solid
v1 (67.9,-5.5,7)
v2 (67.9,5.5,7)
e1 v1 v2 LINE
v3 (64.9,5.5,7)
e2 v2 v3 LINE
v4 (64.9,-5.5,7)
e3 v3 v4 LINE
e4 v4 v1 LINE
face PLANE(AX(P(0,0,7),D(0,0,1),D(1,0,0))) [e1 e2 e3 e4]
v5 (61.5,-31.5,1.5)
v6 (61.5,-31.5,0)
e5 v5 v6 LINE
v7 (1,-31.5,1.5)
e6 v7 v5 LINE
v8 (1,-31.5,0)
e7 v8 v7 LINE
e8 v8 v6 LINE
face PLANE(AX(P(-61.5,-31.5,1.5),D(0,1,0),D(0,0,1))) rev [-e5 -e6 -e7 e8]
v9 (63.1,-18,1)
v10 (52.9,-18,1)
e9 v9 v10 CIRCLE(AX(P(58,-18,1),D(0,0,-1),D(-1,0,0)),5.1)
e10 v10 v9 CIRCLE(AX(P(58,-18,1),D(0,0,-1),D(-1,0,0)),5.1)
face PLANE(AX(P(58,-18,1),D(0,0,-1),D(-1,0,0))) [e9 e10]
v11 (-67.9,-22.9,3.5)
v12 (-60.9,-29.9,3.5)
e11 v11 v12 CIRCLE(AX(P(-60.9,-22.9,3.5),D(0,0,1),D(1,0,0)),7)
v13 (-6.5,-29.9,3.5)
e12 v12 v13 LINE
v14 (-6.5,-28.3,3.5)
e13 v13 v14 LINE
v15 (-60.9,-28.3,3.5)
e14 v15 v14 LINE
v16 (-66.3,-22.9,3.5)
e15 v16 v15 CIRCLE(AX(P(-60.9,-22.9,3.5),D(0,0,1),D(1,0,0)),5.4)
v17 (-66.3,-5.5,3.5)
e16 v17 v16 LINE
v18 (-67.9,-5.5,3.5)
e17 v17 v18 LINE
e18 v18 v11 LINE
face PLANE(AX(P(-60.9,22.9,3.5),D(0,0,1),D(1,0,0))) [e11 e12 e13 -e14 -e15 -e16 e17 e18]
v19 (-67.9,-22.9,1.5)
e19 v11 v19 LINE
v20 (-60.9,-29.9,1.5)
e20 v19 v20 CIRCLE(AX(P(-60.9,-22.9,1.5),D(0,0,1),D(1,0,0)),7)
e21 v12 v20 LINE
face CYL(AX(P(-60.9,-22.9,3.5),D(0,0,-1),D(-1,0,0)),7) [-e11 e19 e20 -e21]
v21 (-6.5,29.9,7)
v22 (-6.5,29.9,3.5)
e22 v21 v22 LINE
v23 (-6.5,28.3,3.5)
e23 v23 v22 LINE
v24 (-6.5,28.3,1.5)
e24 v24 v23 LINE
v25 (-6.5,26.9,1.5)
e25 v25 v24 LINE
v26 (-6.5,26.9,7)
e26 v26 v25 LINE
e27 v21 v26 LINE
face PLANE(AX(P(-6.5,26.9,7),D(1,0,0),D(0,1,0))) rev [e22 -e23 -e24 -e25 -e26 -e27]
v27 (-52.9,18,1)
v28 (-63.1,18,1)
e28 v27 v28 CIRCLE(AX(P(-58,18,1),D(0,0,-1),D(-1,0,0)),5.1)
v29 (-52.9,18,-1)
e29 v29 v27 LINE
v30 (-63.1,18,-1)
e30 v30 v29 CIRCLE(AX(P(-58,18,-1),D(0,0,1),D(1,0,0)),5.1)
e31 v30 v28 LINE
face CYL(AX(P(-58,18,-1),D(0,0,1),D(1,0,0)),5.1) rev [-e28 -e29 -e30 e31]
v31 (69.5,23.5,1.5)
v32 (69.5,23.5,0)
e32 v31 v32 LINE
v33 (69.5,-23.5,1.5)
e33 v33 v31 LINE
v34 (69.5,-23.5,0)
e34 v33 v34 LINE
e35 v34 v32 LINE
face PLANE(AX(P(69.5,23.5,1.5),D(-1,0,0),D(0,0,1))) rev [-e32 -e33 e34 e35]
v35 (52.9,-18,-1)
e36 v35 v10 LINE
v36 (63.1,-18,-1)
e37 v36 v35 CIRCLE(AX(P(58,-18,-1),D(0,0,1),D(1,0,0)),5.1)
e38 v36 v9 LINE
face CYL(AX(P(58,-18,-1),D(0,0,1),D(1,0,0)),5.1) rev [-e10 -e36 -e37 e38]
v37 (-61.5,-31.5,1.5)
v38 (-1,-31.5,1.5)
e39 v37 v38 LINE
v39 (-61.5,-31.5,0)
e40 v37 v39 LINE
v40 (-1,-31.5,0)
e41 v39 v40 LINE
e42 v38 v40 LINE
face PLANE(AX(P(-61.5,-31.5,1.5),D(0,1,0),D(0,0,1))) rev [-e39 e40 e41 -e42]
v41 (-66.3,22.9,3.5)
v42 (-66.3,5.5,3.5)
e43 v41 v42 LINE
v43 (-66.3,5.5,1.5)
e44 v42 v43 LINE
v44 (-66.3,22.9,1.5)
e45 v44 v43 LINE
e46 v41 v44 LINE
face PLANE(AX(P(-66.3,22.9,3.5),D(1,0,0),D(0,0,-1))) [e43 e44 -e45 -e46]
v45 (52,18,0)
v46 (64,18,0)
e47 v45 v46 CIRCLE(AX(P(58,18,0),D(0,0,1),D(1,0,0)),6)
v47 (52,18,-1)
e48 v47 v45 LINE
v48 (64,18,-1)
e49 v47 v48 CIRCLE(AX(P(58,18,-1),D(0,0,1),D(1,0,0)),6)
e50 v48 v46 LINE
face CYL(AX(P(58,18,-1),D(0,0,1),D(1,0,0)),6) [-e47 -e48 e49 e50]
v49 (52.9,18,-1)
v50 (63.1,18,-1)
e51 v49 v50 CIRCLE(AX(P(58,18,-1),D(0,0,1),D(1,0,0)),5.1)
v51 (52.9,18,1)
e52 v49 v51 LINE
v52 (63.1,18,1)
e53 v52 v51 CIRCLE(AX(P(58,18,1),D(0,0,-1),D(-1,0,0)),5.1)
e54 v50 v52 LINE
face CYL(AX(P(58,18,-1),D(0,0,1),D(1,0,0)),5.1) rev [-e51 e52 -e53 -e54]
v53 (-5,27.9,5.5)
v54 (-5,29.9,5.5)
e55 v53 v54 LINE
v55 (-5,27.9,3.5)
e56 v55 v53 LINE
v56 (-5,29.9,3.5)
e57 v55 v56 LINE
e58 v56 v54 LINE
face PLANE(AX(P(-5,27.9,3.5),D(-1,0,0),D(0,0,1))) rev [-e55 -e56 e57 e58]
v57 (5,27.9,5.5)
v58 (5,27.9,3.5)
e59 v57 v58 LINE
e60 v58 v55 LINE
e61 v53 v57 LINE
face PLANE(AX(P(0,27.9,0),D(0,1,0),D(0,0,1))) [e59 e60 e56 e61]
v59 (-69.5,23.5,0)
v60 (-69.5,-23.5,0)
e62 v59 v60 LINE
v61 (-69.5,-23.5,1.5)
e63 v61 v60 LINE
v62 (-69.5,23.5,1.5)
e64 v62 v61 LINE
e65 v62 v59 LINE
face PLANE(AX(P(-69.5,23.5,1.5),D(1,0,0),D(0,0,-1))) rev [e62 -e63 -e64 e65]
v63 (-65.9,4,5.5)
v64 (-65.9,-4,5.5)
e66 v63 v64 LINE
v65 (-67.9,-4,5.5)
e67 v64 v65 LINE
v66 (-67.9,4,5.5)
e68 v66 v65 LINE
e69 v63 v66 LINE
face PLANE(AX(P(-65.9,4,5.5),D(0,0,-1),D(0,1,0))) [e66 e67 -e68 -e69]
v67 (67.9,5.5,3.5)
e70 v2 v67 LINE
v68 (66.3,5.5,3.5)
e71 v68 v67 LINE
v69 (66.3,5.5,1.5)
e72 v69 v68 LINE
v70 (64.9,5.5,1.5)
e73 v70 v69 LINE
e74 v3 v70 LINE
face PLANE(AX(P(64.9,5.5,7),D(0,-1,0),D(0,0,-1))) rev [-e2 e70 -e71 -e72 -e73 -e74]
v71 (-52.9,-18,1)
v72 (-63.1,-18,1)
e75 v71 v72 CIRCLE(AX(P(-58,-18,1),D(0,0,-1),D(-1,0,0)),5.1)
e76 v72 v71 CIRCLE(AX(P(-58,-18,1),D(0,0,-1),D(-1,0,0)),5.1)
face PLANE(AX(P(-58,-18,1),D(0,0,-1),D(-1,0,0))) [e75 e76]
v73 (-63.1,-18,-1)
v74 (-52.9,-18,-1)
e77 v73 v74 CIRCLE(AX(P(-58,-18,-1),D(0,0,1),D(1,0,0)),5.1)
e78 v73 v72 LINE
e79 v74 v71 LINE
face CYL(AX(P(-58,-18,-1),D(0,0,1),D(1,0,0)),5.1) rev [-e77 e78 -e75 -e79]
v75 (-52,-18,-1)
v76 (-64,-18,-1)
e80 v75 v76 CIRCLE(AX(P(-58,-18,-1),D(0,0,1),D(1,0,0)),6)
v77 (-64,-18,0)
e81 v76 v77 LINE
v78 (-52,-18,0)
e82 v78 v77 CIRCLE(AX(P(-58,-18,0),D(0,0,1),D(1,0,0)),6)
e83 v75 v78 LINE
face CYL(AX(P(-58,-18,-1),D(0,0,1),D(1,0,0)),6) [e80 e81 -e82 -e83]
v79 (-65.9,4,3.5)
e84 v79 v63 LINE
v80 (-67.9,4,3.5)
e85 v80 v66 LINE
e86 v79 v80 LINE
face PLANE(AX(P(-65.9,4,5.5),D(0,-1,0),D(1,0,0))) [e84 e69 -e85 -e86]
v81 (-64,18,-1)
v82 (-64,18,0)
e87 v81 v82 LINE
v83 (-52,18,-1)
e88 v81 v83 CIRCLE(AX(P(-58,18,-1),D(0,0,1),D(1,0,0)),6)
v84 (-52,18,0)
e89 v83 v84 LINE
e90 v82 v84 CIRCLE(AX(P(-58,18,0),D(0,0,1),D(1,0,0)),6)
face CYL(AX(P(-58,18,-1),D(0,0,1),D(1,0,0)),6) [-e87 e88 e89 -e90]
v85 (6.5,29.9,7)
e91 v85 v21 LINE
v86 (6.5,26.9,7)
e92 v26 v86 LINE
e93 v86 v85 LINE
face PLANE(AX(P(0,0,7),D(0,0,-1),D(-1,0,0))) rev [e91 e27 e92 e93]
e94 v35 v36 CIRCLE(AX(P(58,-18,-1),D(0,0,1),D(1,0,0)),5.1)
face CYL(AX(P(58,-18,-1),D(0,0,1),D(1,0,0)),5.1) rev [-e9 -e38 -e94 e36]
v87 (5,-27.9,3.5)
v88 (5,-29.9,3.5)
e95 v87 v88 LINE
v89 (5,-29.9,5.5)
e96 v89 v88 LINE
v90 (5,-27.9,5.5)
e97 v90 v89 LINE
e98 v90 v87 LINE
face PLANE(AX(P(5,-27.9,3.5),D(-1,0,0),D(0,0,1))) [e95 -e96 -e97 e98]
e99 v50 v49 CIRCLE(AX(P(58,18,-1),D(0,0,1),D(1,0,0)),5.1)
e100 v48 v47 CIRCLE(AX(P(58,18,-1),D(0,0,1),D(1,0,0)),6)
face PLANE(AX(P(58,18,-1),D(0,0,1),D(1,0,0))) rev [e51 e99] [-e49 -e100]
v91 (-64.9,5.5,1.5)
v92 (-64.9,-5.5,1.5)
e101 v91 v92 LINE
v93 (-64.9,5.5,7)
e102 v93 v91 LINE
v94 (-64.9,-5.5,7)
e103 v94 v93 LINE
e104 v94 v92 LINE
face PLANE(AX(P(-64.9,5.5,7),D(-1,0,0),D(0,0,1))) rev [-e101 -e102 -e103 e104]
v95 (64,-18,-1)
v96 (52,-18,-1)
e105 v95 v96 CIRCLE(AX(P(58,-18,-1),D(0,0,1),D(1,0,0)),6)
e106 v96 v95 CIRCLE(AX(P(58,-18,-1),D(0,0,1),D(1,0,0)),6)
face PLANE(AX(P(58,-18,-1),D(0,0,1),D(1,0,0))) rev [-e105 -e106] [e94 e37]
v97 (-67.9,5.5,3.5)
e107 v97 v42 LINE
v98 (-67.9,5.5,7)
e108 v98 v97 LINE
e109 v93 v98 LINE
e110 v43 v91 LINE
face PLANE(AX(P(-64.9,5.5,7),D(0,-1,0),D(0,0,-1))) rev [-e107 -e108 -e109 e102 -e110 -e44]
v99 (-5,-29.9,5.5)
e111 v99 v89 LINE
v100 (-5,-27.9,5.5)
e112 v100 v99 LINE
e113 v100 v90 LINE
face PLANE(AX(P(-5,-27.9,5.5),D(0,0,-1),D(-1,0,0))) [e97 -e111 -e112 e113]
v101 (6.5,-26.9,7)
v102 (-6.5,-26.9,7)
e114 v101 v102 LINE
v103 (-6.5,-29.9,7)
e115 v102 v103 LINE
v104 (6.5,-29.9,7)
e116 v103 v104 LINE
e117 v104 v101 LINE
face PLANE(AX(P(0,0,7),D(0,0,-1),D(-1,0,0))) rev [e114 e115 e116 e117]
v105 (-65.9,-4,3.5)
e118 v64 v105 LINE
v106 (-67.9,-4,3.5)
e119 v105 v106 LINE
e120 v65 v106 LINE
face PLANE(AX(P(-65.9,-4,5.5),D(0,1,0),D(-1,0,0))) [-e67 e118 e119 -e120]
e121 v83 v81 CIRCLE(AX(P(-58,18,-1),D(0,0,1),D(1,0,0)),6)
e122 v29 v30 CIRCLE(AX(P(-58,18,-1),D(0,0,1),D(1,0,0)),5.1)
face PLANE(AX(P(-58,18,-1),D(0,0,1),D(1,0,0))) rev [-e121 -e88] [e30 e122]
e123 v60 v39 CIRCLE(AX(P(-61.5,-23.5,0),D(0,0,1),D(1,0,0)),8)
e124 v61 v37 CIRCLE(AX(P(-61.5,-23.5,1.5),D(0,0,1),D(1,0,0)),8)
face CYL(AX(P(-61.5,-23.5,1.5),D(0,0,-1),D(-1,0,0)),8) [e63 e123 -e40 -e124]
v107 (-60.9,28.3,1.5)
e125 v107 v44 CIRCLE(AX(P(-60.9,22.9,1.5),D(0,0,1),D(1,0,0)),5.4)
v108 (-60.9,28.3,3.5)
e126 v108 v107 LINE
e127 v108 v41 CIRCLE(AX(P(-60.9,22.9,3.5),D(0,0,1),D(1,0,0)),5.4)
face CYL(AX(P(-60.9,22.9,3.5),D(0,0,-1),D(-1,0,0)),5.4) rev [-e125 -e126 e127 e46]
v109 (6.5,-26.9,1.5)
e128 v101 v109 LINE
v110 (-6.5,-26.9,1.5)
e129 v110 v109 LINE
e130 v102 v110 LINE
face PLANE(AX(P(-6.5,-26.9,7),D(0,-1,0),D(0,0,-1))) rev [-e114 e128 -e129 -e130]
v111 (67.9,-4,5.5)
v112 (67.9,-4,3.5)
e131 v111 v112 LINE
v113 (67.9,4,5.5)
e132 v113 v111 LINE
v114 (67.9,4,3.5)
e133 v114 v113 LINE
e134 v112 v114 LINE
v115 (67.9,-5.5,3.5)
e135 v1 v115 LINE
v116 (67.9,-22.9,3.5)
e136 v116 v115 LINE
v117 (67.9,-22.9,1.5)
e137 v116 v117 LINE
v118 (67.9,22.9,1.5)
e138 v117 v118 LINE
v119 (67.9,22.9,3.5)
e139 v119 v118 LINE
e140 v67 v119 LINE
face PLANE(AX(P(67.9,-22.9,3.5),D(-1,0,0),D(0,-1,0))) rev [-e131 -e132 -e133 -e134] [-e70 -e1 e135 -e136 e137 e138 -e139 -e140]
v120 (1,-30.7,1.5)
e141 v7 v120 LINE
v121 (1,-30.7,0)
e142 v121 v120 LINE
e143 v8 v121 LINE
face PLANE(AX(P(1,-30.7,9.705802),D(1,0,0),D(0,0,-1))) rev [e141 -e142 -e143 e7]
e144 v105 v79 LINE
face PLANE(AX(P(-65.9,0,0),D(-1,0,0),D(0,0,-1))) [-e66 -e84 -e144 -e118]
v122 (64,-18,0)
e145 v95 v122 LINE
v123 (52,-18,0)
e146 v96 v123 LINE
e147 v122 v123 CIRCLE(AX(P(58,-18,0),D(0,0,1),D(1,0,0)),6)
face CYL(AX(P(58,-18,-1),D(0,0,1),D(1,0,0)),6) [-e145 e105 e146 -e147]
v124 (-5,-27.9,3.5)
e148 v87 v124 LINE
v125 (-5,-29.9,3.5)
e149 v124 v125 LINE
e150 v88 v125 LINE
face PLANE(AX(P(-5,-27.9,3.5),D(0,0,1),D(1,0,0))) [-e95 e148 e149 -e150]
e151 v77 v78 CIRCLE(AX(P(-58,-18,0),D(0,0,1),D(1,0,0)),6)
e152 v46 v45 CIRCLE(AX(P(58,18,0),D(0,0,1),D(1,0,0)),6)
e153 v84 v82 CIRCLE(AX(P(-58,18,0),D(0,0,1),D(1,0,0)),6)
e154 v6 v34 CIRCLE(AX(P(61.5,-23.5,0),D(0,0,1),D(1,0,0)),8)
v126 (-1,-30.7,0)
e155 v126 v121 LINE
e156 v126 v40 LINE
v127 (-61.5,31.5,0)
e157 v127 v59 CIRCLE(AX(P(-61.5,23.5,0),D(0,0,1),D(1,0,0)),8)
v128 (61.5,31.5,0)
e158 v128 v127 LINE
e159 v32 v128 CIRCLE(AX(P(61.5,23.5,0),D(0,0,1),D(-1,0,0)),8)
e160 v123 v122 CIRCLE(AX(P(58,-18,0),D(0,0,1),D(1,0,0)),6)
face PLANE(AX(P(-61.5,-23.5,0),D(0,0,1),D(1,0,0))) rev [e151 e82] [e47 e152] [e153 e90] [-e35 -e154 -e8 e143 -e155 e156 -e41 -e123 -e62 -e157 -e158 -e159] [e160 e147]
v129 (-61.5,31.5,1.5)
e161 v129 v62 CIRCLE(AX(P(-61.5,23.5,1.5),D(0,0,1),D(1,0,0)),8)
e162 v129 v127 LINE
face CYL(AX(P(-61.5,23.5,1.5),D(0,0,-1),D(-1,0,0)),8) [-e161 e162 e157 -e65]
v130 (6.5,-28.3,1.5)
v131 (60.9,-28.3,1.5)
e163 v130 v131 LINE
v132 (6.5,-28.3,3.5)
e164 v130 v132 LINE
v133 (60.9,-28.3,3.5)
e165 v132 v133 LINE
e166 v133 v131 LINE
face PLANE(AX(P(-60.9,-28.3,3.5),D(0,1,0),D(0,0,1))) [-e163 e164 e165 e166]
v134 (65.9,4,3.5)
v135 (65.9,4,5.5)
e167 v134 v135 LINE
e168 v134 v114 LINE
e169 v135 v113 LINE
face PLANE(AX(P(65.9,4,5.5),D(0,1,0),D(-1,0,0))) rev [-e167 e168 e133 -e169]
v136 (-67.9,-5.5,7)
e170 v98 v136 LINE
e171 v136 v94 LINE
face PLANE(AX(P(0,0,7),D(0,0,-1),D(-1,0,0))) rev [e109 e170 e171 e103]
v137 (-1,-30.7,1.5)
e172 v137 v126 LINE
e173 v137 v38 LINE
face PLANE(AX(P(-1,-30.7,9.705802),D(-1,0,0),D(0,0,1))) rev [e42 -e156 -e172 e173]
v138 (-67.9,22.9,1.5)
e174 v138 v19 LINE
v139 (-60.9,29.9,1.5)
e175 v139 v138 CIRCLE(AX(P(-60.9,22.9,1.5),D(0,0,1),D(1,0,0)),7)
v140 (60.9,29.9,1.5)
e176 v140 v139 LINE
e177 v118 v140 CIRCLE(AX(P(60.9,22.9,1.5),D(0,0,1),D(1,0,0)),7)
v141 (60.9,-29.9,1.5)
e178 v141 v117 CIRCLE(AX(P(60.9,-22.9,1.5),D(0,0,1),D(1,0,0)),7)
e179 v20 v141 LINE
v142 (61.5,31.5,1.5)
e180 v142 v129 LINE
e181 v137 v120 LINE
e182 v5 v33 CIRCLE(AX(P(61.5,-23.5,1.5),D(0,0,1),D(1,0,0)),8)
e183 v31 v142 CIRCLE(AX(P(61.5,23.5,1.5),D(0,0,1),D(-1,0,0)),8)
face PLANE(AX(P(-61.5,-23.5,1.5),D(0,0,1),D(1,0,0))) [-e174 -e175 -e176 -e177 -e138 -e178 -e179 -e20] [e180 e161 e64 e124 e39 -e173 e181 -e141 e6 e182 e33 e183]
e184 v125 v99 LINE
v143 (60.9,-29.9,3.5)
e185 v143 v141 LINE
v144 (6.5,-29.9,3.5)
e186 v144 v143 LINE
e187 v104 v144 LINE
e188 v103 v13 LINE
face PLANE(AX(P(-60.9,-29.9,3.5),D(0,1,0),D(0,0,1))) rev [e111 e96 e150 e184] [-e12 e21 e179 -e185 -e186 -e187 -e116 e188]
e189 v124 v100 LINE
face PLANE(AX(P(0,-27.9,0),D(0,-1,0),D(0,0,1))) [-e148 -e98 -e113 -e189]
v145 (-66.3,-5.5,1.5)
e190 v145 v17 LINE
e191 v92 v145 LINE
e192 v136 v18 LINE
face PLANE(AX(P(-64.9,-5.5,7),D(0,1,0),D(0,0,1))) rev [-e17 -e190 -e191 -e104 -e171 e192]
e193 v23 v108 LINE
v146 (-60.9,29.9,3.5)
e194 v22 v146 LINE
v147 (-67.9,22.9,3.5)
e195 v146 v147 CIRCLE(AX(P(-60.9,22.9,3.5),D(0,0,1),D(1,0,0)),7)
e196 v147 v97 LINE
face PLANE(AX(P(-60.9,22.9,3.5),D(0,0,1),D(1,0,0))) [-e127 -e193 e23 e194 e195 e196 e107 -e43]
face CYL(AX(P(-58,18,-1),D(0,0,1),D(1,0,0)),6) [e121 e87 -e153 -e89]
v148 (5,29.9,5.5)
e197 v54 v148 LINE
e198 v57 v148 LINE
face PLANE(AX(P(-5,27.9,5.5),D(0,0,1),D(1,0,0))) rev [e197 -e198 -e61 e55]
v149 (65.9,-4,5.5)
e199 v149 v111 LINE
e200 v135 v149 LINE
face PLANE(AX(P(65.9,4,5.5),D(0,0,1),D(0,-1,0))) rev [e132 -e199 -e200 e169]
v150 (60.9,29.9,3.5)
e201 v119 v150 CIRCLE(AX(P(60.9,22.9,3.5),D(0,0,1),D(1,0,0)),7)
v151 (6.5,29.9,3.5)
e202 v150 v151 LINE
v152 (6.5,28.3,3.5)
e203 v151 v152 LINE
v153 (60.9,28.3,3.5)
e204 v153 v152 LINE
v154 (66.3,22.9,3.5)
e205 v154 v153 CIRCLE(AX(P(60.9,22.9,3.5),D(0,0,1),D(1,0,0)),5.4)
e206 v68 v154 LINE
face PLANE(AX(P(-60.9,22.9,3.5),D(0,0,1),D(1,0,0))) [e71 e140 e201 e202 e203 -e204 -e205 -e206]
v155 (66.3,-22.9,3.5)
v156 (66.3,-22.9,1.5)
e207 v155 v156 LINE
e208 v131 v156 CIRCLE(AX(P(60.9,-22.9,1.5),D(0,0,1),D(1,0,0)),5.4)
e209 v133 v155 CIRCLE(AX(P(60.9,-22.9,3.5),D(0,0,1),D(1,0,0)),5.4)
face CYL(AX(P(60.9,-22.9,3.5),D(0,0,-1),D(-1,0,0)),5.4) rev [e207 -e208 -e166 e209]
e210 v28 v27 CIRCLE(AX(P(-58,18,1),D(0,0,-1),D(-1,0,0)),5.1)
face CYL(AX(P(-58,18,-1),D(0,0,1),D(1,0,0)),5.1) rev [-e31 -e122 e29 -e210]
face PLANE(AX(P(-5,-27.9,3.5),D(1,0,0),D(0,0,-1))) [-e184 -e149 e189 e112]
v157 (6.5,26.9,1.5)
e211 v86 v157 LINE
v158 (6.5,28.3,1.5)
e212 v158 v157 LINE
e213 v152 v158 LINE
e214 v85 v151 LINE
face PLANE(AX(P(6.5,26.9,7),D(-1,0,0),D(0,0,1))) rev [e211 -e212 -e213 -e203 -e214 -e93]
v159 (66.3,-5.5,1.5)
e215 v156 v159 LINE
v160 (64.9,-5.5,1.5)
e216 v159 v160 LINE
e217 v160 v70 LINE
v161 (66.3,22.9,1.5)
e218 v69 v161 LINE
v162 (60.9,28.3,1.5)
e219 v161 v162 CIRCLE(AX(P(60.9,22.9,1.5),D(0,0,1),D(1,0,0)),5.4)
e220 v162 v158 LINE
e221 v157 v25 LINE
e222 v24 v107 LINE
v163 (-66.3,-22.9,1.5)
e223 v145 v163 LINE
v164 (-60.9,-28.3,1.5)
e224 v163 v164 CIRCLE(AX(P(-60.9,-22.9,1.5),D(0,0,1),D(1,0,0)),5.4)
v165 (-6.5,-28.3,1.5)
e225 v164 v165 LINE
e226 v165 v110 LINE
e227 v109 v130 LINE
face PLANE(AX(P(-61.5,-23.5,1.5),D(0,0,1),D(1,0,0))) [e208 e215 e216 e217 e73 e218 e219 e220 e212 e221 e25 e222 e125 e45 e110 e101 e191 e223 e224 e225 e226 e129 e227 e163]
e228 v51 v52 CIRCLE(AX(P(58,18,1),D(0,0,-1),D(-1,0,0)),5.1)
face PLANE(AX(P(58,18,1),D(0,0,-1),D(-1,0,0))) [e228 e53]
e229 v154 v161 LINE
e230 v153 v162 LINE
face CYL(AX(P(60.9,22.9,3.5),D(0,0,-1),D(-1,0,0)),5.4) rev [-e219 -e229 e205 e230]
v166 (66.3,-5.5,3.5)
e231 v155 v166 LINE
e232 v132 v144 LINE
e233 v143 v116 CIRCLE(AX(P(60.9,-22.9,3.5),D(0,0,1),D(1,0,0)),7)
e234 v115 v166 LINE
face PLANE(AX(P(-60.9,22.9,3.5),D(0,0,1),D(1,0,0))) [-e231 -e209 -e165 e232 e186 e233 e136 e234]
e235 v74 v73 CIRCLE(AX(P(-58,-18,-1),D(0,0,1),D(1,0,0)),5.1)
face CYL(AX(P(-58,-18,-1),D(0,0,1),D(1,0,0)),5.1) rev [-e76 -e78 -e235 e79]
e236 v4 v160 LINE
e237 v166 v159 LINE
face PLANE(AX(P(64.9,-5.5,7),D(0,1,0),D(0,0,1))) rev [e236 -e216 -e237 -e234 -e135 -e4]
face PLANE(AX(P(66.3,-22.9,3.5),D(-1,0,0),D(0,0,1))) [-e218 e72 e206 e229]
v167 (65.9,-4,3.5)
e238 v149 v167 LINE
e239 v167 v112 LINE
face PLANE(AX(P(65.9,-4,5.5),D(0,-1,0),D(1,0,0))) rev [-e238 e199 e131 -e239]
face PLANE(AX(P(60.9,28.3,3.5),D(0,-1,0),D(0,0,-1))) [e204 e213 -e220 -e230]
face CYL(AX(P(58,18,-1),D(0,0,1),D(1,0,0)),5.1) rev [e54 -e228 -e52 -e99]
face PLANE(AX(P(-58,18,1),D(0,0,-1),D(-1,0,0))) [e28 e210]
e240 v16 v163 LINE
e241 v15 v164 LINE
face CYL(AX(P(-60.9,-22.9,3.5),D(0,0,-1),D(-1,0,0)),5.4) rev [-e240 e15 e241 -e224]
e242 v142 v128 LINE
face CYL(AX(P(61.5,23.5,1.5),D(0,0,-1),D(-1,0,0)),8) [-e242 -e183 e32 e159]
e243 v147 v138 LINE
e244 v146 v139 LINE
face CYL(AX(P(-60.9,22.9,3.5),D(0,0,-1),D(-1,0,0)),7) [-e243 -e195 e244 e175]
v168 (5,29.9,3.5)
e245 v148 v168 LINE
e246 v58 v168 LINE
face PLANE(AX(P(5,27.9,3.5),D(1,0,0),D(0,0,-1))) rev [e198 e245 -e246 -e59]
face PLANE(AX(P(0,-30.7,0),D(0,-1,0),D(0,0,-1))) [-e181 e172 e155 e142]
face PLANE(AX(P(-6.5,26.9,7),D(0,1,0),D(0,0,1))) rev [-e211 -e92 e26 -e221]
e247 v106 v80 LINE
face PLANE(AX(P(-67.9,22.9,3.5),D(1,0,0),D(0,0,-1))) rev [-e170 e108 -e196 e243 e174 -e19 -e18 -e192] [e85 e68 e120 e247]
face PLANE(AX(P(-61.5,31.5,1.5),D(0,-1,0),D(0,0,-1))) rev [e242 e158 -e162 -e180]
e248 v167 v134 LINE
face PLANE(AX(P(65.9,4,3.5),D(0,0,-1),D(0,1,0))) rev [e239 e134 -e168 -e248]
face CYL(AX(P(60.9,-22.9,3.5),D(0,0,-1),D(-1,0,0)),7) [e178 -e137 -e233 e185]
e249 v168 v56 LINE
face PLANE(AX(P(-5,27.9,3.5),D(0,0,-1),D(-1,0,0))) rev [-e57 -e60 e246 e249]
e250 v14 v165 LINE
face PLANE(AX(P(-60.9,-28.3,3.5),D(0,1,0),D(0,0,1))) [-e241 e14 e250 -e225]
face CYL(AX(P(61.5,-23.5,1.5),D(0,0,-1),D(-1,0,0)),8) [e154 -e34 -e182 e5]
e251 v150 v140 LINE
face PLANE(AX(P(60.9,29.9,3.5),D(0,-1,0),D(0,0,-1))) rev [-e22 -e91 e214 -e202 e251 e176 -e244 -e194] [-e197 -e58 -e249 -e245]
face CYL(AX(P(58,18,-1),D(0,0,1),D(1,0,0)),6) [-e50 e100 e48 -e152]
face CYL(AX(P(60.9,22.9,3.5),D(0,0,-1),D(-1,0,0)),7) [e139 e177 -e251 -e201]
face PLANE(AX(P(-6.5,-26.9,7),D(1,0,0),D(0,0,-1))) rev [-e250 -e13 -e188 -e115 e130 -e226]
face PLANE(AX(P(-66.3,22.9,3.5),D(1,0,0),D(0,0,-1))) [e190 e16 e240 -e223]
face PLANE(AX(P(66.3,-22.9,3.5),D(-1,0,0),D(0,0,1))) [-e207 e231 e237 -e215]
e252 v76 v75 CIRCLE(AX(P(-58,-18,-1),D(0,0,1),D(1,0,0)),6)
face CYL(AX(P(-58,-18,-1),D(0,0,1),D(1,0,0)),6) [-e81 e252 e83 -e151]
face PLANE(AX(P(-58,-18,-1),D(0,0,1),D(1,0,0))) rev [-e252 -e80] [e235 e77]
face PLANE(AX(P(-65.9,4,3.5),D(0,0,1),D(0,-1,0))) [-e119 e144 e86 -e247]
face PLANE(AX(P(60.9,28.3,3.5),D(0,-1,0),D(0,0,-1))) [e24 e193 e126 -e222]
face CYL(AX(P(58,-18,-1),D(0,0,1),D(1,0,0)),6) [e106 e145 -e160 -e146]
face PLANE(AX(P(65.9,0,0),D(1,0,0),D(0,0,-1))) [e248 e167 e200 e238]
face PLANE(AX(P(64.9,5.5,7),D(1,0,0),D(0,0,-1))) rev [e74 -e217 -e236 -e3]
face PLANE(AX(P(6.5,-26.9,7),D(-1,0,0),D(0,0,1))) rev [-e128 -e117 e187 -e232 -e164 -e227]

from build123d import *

# Parameters (mm, degrees)
BOSS_EXTRUDE1_DEPTH = 1.5
BOSS_EXTRUDE2_START = -1.5
SKETCH2_R           = 6
SKETCH2_R_2         = 5.1
BOSS_EXTRUDE2_DEPTH = 1
BOSS_EXTRUDE3_DEPTH = 2
SKETCH4_W           = 13
SKETCH4_H           = 3
SKETCH4_W_2         = 3
SKETCH4_H_2         = 11
BOSS_EXTRUDE4_DEPTH = 3.5
SKETCH5_W           = 10
SKETCH5_H           = 2
CUT_EXTRUDE1_DEPTH  = 2
SKETCH7_W           = 2
SKETCH7_H           = 19.411603012
CUT_EXTRUDE3_DEPTH  = 0.8
CUT_EXTRUDE4_START  = -1
SKETCH8_R           = 5.1
CUT_EXTRUDE4_DEPTH  = 1
SKETCH9_W           = 2
SKETCH9_H           = 8
CUT_EXTRUDE5_DEPTH  = 2


with BuildPart() as part:
    # Sketch1 → Boss-Extrude1 (new body)
    with BuildSketch(Plane.XY):
        with BuildLine():
            Line((-61.5, 31.5), (61.5, 31.5))
            ThreePointArc((61.5, 31.5), (67.156854249, 29.156854249), (69.5, 23.5))
            Line((69.5, 23.5), (69.5, -23.5))
            ThreePointArc((69.5, -23.5), (67.156854249, -29.156854249), (61.5, -31.5))
            Line((61.5, -31.5), (-61.5, -31.5))
            ThreePointArc((-61.5, -31.5), (-67.156854249, -29.156854249), (-69.5, -23.5))
            Line((-69.5, -23.5), (-69.5, 23.5))
            ThreePointArc((-69.5, 23.5), (-67.156854249, 29.156854249), (-61.5, 31.5))
        make_face()
    extrude(amount=BOSS_EXTRUDE1_DEPTH)

    # Sketch2 → Boss-Extrude2 (add)
    # profile 1 of 4: a face of its own
    with BuildSketch(Plane.XY.offset(1.5).offset(BOSS_EXTRUDE2_START)):
        with Locations((-58, 18)):
            Circle(SKETCH2_R)
        with Locations((-58, 18)):
            Circle(SKETCH2_R_2, mode=Mode.SUBTRACT)
    # profile 2 of 4: a face of its own
    with BuildSketch(Plane.XY.offset(1.5).offset(BOSS_EXTRUDE2_START)):
        with Locations((58, 18)):
            Circle(SKETCH2_R)
        with Locations((58, 18)):
            Circle(SKETCH2_R_2, mode=Mode.SUBTRACT)
    # profile 3 of 4: a face of its own
    with BuildSketch(Plane.XY.offset(1.5).offset(BOSS_EXTRUDE2_START)):
        with Locations((-58, -18)):
            Circle(SKETCH2_R)
        with Locations((-58, -18)):
            Circle(SKETCH2_R_2, mode=Mode.SUBTRACT)
    # profile 4 of 4: a face of its own
    with BuildSketch(Plane.XY.offset(1.5).offset(BOSS_EXTRUDE2_START)):
        with Locations((58, -18)):
            Circle(SKETCH2_R)
        with Locations((58, -18)):
            Circle(SKETCH2_R_2, mode=Mode.SUBTRACT)
    extrude(amount=-BOSS_EXTRUDE2_DEPTH)

    # Sketch3 → Boss-Extrude3 (add)
    with BuildSketch(Plane.XY.offset(1.5)):
        with BuildLine():
            Line((60.9, 29.9), (-60.9, 29.9))
            ThreePointArc((-60.9, 29.9), (-65.849747468, 27.849747468), (-67.9, 22.9))
            Line((-67.9, 22.9), (-67.9, -22.9))
            ThreePointArc((-67.9, -22.9), (-65.849747468, -27.849747468), (-60.9, -29.9))
            Line((-60.9, -29.9), (60.9, -29.9))
            ThreePointArc((60.9, -29.9), (65.849747468, -27.849747468), (67.9, -22.9))
            Line((67.9, -22.9), (67.9, 22.9))
            ThreePointArc((67.9, 22.9), (65.849747468, 27.849747468), (60.9, 29.9))
        make_face()
        with BuildLine():
            Line((60.9, 28.3), (-60.9, 28.3))
            ThreePointArc((-60.9, 28.3), (-64.718376618, 26.718376618), (-66.3, 22.9))
            Line((-66.3, 22.9), (-66.3, -22.9))
            ThreePointArc((-66.3, -22.9), (-64.718376618, -26.718376618), (-60.9, -28.3))
            Line((-60.9, -28.3), (60.9, -28.3))
            ThreePointArc((60.9, -28.3), (64.718376618, -26.718376618), (66.3, -22.9))
            Line((66.3, -22.9), (66.3, 22.9))
            ThreePointArc((66.3, 22.9), (64.718376618, 26.718376618), (60.9, 28.3))
        make_face(mode=Mode.SUBTRACT)
    extrude(amount=BOSS_EXTRUDE3_DEPTH)

    # Sketch4 → Boss-Extrude4 (add, symmetric)
    with BuildSketch(Plane.XY.offset(3.5)):
        with Locations((0, 28.4)):
            Rectangle(SKETCH4_W, SKETCH4_H)
        with Locations((0, -28.4)):
            Rectangle(SKETCH4_W, SKETCH4_H)
        with Locations((66.4, 0)):
            Rectangle(SKETCH4_W_2, SKETCH4_H_2)
        with Locations((-66.4, 0)):
            Rectangle(SKETCH4_W_2, SKETCH4_H_2)
    extrude(amount=BOSS_EXTRUDE4_DEPTH, both=True)

    # Sketch5 → Cut-Extrude1 (cut)
    with BuildSketch(Plane(origin=(0, 29.9, 0), x_dir=(1, 0, 0), z_dir=(0, 1, 0))):
        with Locations((0, -4.5)):
            Rectangle(SKETCH5_W, SKETCH5_H)
    cut_extrude1 = extrude(amount=-CUT_EXTRUDE1_DEPTH, mode=Mode.SUBTRACT)

    # Mirror1: Cut-Extrude1 across plane
    add(cut_extrude1.mirror(Plane.ZX), mode=Mode.SUBTRACT)

    # Sketch7 → Cut-Extrude3 (cut)
    with BuildSketch(Plane(origin=(0, -31.5, 0), x_dir=(-1, 0, 0), z_dir=(0, -1, 0))):
        Rectangle(SKETCH7_W, SKETCH7_H)
    extrude(amount=-CUT_EXTRUDE3_DEPTH, mode=Mode.SUBTRACT)

    # Sketch8 → Cut-Extrude4 (cut)
    with BuildSketch(Plane(origin=(0, 0, 0), x_dir=(-1, 0, 0), z_dir=(0, 0, -1)).offset(CUT_EXTRUDE4_START)):
        with Locations(Location((-58, 18, 0), (0, 0, 180))):
            Circle(SKETCH8_R)
        with Locations(Location((58, 18, 0), (0, 0, 180))):
            Circle(SKETCH8_R)
        with Locations(Location((58, -18, 0), (0, 0, 180))):
            Circle(SKETCH8_R)
        with Locations(Location((-58, -18, 0), (0, 0, 180))):
            Circle(SKETCH8_R)
    extrude(amount=CUT_EXTRUDE4_DEPTH, mode=Mode.SUBTRACT)

    # Sketch9 → Cut-Extrude5 (cut)
    with BuildSketch(Plane(origin=(67.9, 0, 0), x_dir=(0, 0, -1), z_dir=(1, 0, 0))):
        with Locations((-4.5, 0)):
            Rectangle(SKETCH9_W, SKETCH9_H)
    cut_extrude5 = extrude(amount=-CUT_EXTRUDE5_DEPTH, mode=Mode.SUBTRACT)

    # Mirror2: Cut-Extrude5 across plane
    add(cut_extrude5.mirror(Plane(origin=(0, 0, 0), x_dir=(0, 0, 1), z_dir=(1, 0, 0))), mode=Mode.SUBTRACT)


solid = part.part
